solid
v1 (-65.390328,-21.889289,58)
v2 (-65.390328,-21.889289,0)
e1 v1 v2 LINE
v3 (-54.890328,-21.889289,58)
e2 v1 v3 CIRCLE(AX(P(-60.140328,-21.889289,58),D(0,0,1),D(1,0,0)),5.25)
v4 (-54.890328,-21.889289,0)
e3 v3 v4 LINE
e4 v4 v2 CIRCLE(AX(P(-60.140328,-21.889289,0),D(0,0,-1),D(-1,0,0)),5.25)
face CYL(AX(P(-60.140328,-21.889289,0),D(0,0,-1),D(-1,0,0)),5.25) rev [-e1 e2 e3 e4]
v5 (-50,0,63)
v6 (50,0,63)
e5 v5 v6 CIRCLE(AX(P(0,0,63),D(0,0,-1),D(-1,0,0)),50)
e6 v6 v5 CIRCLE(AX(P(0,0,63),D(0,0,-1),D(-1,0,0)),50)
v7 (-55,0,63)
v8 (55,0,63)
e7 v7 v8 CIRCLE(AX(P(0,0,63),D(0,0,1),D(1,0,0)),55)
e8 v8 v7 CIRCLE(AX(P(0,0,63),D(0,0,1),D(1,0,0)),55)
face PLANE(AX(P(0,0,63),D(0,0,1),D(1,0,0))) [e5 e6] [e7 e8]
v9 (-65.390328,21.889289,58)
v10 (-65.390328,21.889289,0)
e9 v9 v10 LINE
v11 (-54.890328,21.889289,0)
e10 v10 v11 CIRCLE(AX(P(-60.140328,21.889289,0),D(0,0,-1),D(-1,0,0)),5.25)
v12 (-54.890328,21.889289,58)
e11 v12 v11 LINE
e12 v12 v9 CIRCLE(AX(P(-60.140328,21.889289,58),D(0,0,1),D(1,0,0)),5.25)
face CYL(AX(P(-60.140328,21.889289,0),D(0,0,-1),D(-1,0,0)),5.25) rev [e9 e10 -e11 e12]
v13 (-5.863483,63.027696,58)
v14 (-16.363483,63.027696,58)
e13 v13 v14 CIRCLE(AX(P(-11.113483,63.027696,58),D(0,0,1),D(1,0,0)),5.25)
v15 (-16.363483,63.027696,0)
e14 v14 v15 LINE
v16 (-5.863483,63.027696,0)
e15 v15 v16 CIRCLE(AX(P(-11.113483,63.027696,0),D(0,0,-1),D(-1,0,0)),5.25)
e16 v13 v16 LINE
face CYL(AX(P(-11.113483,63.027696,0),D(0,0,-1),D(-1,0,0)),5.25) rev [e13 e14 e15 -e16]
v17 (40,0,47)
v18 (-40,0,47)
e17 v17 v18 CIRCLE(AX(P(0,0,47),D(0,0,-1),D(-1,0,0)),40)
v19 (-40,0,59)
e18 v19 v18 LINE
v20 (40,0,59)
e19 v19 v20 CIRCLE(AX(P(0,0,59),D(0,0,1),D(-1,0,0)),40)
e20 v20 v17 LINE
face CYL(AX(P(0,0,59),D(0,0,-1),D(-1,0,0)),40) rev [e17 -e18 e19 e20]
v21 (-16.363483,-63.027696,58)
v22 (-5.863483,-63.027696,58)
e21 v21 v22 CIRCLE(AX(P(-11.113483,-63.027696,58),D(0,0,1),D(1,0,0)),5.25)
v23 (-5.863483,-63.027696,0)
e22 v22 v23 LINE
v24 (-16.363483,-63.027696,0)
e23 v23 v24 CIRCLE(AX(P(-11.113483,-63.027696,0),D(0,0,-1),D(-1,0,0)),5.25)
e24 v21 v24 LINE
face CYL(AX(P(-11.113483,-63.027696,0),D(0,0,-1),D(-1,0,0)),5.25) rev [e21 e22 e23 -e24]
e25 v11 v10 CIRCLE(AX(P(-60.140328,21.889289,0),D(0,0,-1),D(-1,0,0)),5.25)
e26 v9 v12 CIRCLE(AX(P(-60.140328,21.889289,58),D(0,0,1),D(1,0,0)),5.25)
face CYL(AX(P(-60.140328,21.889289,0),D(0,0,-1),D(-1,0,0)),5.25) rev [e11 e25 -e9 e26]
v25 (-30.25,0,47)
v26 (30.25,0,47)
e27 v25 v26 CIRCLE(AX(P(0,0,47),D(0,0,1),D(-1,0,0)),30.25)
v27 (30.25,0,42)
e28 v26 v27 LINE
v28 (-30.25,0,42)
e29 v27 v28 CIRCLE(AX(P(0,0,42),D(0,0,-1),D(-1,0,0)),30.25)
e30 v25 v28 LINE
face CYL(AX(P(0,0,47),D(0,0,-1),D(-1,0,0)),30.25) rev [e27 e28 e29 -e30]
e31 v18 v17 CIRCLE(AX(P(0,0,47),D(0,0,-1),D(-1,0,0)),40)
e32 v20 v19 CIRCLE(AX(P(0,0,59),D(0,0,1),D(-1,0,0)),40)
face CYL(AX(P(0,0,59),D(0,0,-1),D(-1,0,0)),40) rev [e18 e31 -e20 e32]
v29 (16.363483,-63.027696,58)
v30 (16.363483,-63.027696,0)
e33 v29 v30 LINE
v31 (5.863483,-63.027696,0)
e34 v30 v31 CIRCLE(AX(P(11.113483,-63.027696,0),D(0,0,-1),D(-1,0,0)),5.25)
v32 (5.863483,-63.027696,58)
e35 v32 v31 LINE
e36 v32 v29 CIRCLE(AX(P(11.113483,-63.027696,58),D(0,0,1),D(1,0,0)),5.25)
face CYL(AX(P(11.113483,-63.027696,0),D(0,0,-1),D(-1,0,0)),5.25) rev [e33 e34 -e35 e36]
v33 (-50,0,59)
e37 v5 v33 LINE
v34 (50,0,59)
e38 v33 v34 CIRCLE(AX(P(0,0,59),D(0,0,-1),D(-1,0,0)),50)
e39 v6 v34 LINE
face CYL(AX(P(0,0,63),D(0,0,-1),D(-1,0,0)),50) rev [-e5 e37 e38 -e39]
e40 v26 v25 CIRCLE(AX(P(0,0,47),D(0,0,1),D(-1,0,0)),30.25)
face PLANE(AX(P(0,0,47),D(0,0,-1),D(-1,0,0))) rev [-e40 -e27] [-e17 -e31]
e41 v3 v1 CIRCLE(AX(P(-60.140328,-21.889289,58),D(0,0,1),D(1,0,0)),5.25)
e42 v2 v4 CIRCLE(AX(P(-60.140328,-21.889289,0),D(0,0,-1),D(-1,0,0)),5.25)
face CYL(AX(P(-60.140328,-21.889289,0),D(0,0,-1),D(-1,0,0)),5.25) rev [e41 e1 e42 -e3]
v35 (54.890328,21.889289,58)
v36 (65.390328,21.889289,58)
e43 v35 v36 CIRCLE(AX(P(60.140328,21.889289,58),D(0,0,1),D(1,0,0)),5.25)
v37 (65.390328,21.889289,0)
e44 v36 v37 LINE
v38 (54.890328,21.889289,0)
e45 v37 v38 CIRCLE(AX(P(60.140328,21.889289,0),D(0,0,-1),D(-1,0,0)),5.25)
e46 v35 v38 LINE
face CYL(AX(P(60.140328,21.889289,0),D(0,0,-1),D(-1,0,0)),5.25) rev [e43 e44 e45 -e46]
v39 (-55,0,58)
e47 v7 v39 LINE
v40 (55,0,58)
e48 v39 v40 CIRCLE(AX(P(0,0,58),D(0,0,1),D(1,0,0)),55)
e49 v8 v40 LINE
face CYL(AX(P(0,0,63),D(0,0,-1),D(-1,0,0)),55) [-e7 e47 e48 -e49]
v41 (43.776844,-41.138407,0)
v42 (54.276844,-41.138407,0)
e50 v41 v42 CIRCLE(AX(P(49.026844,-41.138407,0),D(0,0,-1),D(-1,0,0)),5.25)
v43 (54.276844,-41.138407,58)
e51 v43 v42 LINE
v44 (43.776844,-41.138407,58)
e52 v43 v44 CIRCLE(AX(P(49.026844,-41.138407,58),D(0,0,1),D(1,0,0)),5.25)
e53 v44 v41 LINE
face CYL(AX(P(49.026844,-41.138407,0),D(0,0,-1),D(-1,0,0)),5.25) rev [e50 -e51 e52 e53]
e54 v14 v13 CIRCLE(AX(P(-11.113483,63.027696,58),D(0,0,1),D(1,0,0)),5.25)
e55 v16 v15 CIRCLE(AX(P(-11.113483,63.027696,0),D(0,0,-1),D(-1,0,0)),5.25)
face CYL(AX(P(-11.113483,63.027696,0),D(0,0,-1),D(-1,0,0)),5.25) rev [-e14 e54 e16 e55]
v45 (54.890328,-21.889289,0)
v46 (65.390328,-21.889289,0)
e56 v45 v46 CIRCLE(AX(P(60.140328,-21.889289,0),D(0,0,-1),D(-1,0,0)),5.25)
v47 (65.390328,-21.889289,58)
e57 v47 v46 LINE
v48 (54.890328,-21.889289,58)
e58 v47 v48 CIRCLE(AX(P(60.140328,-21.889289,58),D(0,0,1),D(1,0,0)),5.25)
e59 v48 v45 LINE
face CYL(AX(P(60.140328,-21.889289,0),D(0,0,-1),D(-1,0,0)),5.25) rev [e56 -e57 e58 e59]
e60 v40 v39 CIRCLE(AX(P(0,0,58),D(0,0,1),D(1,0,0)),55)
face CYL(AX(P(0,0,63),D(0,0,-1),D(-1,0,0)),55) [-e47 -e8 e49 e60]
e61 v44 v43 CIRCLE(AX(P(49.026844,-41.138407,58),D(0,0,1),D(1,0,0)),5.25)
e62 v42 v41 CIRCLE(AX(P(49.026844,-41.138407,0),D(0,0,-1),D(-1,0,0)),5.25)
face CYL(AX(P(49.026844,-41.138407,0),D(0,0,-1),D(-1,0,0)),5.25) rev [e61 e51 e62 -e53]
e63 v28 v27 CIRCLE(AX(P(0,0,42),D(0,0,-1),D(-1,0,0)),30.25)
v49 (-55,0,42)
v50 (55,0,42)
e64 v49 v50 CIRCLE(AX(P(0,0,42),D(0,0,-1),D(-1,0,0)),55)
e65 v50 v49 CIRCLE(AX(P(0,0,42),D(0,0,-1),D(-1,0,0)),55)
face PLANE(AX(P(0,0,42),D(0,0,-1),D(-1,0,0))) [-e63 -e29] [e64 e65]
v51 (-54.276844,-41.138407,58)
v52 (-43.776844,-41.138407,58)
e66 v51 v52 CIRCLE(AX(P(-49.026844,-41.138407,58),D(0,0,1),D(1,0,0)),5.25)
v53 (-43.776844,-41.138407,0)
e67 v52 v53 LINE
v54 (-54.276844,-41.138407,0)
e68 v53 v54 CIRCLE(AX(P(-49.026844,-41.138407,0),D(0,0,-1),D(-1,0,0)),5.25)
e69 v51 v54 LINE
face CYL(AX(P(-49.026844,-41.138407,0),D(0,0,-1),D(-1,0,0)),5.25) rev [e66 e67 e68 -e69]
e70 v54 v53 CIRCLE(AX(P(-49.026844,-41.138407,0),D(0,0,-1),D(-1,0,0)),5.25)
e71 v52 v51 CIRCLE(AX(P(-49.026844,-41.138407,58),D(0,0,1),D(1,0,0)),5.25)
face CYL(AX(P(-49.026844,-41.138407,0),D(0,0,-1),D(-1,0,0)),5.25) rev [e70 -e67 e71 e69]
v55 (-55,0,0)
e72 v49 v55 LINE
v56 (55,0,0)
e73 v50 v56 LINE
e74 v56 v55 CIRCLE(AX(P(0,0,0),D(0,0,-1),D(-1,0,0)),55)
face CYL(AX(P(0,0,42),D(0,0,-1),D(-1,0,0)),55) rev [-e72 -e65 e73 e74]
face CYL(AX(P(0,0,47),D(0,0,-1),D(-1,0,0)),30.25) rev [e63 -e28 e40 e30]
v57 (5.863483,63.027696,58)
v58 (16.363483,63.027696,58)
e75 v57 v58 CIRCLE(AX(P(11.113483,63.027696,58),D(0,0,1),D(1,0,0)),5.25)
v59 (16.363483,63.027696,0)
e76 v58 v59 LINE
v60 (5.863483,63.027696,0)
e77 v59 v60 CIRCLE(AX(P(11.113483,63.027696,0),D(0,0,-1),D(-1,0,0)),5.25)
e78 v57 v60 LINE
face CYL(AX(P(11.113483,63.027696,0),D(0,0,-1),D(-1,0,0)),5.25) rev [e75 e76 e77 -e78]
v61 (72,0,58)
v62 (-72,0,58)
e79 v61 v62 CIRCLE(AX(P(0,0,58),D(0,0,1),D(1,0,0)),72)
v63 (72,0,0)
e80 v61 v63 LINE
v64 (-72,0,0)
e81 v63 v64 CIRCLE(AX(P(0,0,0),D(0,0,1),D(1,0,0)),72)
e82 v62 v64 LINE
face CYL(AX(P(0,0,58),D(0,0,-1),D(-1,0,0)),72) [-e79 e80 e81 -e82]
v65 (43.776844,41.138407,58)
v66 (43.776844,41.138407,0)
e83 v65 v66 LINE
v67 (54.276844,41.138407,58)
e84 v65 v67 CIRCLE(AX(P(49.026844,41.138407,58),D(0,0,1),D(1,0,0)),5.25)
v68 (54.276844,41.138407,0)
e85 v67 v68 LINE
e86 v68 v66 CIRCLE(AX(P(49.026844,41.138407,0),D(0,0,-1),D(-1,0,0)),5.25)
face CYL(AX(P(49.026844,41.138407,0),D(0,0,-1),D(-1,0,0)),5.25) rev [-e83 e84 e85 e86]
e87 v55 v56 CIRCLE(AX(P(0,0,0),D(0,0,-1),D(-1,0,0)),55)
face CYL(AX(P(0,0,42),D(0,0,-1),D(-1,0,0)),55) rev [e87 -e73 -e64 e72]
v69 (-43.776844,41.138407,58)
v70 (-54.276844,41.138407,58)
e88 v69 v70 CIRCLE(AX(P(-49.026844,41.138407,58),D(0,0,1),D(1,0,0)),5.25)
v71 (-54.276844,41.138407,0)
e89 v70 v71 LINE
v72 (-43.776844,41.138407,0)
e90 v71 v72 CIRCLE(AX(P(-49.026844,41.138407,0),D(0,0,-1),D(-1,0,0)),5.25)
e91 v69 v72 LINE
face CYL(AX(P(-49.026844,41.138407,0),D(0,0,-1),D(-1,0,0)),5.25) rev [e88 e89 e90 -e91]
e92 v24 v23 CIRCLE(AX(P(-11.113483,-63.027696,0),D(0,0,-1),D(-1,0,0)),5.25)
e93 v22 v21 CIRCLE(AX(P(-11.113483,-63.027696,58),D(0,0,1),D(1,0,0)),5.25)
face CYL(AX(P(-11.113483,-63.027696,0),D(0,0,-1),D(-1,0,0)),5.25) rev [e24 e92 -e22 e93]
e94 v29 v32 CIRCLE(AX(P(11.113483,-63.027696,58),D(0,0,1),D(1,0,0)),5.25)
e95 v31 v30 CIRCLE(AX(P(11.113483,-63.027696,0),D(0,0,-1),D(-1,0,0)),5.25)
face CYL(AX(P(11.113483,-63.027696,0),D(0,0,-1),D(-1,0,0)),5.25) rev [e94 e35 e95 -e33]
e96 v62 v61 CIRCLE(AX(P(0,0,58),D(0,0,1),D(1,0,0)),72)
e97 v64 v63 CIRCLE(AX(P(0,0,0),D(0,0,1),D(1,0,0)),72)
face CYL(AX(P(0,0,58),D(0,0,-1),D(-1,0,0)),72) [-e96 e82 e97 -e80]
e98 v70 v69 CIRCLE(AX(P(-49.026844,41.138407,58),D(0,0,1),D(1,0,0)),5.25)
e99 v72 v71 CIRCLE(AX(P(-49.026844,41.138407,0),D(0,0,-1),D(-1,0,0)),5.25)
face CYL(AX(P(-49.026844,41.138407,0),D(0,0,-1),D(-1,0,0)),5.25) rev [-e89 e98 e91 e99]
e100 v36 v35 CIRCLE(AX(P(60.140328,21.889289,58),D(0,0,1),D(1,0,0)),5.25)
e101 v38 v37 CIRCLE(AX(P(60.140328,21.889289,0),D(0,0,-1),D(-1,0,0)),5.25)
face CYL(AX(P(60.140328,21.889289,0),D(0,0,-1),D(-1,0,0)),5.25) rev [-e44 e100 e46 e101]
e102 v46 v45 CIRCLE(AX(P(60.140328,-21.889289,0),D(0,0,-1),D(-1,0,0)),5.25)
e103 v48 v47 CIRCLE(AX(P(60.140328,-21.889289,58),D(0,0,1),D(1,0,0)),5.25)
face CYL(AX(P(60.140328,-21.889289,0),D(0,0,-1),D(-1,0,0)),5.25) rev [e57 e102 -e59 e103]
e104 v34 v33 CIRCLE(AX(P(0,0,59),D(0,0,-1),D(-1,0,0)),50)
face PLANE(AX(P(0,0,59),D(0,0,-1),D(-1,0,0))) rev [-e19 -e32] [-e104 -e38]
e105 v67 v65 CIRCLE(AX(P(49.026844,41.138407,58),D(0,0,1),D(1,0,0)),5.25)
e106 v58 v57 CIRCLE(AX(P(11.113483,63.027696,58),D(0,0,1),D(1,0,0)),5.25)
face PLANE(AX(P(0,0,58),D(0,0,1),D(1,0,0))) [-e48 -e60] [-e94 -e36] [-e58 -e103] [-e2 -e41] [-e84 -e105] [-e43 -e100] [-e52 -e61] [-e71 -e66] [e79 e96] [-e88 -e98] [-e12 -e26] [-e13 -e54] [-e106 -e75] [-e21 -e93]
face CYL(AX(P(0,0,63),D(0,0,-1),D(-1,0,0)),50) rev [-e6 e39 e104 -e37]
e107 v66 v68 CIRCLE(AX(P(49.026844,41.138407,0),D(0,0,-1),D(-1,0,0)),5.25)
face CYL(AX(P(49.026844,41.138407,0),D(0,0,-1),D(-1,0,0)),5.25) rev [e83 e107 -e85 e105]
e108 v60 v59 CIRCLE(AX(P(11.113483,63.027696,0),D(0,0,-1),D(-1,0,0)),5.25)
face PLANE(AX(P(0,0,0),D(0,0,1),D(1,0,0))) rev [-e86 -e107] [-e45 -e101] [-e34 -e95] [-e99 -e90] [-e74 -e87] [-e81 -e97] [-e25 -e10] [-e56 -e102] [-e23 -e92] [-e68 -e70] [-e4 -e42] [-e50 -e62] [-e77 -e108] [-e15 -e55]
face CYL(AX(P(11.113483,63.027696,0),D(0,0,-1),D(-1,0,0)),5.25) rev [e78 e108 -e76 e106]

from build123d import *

# Parameters (mm, degrees)
SKETCH1_R                    = 72
BOSS_EXTRUDE1_DEPTH          = 58
SKETCH2_R                    = 55
BOSS_EXTRUDE2_DEPTH          = 5
F_10_5_10_5_DIAMETER_HOLE1_D = 10.5
SKETCH5_R                    = 55
CUT_EXTRUDE1_DEPTH           = 42
SKETCH6_R                    = 30.25
CUT_EXTRUDE2_DEPTH           = 5
SKETCH7_R                    = 40
CUT_EXTRUDE3_DEPTH           = 12
SKETCH9_R                    = 50
CUT_EXTRUDE4_DEPTH           = 4


with BuildPart() as part:
    # Sketch1 → Boss-Extrude1 (new body)
    with BuildSketch(Plane.XY):
        with Locations(Location((0, 0, 0), (0, 0, 180))):
            Circle(SKETCH1_R)
    extrude(amount=BOSS_EXTRUDE1_DEPTH)

    # Sketch2 → Boss-Extrude2 (add)
    with BuildSketch(Plane.XY.offset(58)):
        Circle(SKETCH2_R)
    extrude(amount=BOSS_EXTRUDE2_DEPTH)

    # Ø10.5 (10.5) Diameter Hole1 (through all)
    with Locations(Plane(origin=(0, 0, 0), x_dir=(-1, 0, 0), z_dir=(0, 0, -1))):
        with Locations((-11.113483371, 63.027696193), (11.113483371, 63.027696193), (49.02684436, 41.13840702), (60.14032773, 21.889289173), (60.14032773, -21.889289173), (49.02684436, -41.13840702), (11.113483371, -63.027696193), (-11.113483371, -63.027696193), (-49.02684436, -41.13840702), (-60.14032773, -21.889289173), (-60.14032773, 21.889289173), (-49.02684436, 41.13840702)):
            Hole(F_10_5_10_5_DIAMETER_HOLE1_D / 2)

    # Sketch5 → Cut-Extrude1 (cut)
    with BuildSketch(Plane(origin=(0, 0, 0), x_dir=(-1, 0, 0), z_dir=(0, 0, -1))):
        with Locations(Location((0, 0, 0), (0, 0, 180))):
            Circle(SKETCH5_R)
    extrude(amount=-CUT_EXTRUDE1_DEPTH, mode=Mode.SUBTRACT)

    # Sketch6 → Cut-Extrude2 (cut)
    with BuildSketch(Plane(origin=(0, 0, 42), x_dir=(-1, 0, 0), z_dir=(0, 0, -1))):
        Circle(SKETCH6_R)
    extrude(amount=-CUT_EXTRUDE2_DEPTH, mode=Mode.SUBTRACT)

    # Sketch7 → Cut-Extrude3 (cut)
    with BuildSketch(Plane(origin=(0, 0, 47), x_dir=(-1, 0, 0), z_dir=(0, 0, -1))):
        Circle(SKETCH7_R)
    extrude(amount=-CUT_EXTRUDE3_DEPTH, mode=Mode.SUBTRACT)

    # Sketch9 → Cut-Extrude4 (cut)
    with BuildSketch(Plane(origin=(0, 0, 59), x_dir=(-1, 0, 0), z_dir=(0, 0, -1))):
        Circle(SKETCH9_R)
    extrude(amount=-CUT_EXTRUDE4_DEPTH, mode=Mode.SUBTRACT)


solid = part.part
